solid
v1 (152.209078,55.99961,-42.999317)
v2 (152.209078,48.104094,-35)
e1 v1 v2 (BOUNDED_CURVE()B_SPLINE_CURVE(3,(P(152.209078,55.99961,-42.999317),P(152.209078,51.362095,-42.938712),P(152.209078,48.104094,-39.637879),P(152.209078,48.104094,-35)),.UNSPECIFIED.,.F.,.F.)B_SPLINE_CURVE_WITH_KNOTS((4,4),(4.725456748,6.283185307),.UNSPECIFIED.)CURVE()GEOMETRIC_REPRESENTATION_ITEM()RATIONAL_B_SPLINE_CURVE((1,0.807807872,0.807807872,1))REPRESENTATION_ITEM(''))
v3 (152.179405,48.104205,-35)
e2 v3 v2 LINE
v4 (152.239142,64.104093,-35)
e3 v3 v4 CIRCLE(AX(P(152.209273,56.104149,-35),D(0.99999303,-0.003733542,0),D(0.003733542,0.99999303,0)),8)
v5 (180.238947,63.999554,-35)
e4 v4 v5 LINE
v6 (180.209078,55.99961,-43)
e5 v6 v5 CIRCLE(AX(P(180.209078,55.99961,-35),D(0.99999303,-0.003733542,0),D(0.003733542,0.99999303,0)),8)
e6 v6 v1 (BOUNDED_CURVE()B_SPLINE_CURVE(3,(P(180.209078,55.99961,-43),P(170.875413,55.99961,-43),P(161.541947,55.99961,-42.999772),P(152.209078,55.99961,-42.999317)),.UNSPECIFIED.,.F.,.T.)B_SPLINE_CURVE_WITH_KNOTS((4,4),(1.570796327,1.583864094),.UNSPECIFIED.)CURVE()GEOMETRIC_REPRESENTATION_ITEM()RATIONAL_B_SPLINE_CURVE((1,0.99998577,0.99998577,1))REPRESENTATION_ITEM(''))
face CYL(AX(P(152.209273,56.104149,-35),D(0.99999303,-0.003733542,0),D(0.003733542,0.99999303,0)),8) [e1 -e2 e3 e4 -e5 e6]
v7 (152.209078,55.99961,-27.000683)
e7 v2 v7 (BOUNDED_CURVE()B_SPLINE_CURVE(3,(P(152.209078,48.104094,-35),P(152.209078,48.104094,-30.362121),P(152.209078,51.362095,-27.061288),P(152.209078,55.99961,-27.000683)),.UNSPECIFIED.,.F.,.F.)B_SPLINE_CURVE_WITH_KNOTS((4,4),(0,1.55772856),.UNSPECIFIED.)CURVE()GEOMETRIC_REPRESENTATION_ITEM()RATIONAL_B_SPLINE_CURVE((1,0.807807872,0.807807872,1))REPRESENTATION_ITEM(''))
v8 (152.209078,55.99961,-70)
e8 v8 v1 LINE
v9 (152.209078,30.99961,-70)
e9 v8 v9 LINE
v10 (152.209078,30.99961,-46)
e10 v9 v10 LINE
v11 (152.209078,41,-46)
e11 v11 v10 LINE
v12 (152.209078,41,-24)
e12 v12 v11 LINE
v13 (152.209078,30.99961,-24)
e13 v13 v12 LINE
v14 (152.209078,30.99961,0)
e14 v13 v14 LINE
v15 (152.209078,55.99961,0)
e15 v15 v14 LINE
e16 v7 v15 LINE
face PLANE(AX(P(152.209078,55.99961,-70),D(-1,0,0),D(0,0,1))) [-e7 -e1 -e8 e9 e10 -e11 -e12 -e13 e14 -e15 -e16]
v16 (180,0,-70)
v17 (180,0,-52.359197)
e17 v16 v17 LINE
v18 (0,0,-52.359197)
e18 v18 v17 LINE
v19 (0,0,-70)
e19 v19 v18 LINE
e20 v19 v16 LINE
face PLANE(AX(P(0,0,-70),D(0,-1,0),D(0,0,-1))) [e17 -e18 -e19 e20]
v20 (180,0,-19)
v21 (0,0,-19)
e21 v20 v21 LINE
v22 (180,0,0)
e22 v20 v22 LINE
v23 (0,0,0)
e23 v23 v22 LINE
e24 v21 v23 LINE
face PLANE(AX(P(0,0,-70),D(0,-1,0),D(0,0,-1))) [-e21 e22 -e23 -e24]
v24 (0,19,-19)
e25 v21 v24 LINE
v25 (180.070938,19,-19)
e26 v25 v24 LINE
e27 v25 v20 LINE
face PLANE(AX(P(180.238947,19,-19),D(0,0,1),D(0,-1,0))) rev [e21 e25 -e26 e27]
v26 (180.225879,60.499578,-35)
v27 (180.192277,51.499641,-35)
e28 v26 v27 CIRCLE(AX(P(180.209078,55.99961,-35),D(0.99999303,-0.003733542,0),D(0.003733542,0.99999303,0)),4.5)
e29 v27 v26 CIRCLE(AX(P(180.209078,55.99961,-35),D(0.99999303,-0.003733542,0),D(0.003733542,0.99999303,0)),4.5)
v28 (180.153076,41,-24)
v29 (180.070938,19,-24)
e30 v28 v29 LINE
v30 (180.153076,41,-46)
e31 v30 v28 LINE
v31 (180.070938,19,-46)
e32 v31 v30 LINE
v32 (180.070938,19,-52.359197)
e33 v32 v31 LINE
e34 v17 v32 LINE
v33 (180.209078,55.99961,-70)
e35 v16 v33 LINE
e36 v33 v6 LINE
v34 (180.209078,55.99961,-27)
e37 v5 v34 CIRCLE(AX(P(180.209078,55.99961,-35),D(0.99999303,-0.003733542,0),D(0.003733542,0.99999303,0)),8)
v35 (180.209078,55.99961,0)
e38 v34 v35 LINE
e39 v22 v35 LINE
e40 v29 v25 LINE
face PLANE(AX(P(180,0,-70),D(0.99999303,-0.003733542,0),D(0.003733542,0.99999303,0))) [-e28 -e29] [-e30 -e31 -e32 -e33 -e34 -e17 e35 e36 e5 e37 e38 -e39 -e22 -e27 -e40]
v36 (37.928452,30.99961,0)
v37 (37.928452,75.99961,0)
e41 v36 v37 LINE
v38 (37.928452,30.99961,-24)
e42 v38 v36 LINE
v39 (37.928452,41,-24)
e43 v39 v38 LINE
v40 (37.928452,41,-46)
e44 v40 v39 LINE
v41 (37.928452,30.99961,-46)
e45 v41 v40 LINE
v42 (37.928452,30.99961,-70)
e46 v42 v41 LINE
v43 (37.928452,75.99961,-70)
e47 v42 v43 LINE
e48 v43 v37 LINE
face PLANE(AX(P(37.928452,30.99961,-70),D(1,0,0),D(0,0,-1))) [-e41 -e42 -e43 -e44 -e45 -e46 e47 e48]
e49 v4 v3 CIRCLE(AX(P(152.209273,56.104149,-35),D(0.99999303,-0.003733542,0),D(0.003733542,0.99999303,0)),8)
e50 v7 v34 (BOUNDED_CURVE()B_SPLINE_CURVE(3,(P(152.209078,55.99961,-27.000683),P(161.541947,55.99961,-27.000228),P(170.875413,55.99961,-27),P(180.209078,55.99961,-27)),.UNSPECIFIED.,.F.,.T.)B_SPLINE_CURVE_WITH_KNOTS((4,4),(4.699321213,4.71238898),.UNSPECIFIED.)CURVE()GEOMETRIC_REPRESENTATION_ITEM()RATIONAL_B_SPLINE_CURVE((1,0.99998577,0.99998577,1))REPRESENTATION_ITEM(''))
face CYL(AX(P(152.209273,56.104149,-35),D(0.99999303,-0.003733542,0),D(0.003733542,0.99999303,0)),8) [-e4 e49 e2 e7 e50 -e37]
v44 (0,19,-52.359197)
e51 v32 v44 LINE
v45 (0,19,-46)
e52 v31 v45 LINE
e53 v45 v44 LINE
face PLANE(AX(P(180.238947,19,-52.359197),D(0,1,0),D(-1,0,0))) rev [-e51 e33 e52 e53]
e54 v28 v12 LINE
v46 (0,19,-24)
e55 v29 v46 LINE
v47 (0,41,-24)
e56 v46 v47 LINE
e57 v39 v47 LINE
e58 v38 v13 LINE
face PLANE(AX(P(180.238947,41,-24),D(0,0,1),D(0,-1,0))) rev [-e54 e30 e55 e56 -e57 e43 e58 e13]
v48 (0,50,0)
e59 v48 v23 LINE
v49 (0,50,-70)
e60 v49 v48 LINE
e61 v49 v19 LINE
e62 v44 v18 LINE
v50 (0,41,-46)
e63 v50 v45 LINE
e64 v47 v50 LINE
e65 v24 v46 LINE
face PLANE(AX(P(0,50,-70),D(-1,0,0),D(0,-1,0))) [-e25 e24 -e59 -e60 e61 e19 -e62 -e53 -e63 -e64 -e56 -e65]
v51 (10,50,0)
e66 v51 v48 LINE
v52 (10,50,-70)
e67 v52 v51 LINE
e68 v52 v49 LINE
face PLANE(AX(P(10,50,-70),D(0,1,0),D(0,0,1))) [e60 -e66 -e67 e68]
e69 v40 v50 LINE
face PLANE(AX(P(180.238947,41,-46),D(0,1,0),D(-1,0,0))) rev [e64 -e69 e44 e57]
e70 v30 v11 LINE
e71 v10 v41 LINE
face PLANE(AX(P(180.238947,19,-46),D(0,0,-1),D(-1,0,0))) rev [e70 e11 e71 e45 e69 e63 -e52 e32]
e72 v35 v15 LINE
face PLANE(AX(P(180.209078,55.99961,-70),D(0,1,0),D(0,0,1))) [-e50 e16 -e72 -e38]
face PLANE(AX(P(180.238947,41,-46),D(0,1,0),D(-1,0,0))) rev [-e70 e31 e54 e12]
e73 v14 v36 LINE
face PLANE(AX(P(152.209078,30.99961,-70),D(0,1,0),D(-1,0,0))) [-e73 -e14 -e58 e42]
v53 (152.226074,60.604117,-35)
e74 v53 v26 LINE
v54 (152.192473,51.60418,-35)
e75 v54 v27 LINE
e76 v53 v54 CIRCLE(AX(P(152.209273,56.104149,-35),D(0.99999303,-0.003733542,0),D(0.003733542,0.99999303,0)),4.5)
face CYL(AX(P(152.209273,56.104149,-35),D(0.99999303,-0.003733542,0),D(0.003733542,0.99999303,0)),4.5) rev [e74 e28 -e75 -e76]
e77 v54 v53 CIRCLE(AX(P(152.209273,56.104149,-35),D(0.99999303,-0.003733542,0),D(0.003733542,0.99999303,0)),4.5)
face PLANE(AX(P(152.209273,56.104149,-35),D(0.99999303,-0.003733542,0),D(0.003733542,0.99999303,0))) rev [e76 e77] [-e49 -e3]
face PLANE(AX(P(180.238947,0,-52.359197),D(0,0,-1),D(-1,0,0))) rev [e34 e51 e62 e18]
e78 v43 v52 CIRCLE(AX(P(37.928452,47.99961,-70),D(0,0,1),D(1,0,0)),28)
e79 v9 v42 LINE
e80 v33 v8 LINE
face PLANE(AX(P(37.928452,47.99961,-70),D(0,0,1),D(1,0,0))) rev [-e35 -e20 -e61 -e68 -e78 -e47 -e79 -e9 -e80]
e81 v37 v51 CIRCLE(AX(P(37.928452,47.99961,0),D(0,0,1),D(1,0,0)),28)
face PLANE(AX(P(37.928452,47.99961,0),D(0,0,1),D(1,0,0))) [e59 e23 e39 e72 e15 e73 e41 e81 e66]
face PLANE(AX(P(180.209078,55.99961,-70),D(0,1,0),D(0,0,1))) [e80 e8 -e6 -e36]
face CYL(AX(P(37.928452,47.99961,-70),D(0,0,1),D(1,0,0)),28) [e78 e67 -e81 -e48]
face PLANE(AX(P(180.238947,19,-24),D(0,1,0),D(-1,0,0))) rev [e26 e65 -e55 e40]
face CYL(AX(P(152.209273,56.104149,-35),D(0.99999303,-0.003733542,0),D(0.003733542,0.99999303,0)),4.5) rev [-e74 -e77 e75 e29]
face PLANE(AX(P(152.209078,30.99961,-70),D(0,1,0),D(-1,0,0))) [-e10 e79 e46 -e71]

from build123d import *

# Parameters (mm, degrees)
BASE_BODY_DEPTH    = 70
PIN_BOSS_SKETCH_R  = 8
PIN_BOSS_DEPTH     = 28
PIN_HOLE_SKETCH_R  = 4.5
PIN_HOLE_DEPTH     = 28
END_SLOT_CUT_DEPTH = 208.754707688


with BuildPart() as part:
    # Base Profile Sketch → Base Body (new body)
    with BuildSketch(Plane.XY):
        with BuildLine():
            Line((0, 0), (180, 0))
            Line((180, 0), (180.209078325, 55.999609697))
            Line((180.209078325, 55.999609697), (152.209078325, 55.999609697))
            Line((152.209078325, 55.999609697), (152.209078325, 30.999609697))
            Line((152.209078325, 30.999609697), (37.928452135, 30.999609697))
            Line((37.928452135, 30.999609697), (37.928452135, 75.999609697))
            ThreePointArc((37.928452135, 75.999609697), (18.849811309, 68.493644543), (10, 50))
            Line((10, 50), (0, 50))
            Line((0, 50), (0, 0))
        make_face()
    extrude(amount=-BASE_BODY_DEPTH)

    # Pin Boss Sketch → Pin Boss (add)
    with BuildSketch(Plane(origin=(179.99749092, -0.67203279, 0), x_dir=(0, 0, -1), z_dir=(0.9999930303095579, -0.0037335415234940133, 0))):
        with Locations(Location((35, 56.672037474, 0), (0, 0, 90))):
            Circle(PIN_BOSS_SKETCH_R)
    extrude(amount=-PIN_BOSS_DEPTH)

    # Pin Hole Sketch → Pin Hole (cut)
    with BuildSketch(Plane(origin=(179.99749092, -0.67203279, 0), x_dir=(0, 0, -1), z_dir=(0.9999930303095579, -0.0037335415234940133, 0))):
        with Locations(Location((35, 56.672037474, 0), (0, 0, 90))):
            Circle(PIN_HOLE_SKETCH_R)
    extrude(amount=-PIN_HOLE_DEPTH, mode=Mode.SUBTRACT)

    # End Slot Sketch → End Slot Cut (cut, through all)
    with BuildSketch(Plane.ZY):
        Polygon((-52.359197148, 0), (-52.359197148, 19), (-46, 19), (-46, 41), (-24, 41), (-24, 19), (-19, 19), (-19, 0), align=None)
    extrude(amount=-END_SLOT_CUT_DEPTH, mode=Mode.SUBTRACT)


solid = part.part
